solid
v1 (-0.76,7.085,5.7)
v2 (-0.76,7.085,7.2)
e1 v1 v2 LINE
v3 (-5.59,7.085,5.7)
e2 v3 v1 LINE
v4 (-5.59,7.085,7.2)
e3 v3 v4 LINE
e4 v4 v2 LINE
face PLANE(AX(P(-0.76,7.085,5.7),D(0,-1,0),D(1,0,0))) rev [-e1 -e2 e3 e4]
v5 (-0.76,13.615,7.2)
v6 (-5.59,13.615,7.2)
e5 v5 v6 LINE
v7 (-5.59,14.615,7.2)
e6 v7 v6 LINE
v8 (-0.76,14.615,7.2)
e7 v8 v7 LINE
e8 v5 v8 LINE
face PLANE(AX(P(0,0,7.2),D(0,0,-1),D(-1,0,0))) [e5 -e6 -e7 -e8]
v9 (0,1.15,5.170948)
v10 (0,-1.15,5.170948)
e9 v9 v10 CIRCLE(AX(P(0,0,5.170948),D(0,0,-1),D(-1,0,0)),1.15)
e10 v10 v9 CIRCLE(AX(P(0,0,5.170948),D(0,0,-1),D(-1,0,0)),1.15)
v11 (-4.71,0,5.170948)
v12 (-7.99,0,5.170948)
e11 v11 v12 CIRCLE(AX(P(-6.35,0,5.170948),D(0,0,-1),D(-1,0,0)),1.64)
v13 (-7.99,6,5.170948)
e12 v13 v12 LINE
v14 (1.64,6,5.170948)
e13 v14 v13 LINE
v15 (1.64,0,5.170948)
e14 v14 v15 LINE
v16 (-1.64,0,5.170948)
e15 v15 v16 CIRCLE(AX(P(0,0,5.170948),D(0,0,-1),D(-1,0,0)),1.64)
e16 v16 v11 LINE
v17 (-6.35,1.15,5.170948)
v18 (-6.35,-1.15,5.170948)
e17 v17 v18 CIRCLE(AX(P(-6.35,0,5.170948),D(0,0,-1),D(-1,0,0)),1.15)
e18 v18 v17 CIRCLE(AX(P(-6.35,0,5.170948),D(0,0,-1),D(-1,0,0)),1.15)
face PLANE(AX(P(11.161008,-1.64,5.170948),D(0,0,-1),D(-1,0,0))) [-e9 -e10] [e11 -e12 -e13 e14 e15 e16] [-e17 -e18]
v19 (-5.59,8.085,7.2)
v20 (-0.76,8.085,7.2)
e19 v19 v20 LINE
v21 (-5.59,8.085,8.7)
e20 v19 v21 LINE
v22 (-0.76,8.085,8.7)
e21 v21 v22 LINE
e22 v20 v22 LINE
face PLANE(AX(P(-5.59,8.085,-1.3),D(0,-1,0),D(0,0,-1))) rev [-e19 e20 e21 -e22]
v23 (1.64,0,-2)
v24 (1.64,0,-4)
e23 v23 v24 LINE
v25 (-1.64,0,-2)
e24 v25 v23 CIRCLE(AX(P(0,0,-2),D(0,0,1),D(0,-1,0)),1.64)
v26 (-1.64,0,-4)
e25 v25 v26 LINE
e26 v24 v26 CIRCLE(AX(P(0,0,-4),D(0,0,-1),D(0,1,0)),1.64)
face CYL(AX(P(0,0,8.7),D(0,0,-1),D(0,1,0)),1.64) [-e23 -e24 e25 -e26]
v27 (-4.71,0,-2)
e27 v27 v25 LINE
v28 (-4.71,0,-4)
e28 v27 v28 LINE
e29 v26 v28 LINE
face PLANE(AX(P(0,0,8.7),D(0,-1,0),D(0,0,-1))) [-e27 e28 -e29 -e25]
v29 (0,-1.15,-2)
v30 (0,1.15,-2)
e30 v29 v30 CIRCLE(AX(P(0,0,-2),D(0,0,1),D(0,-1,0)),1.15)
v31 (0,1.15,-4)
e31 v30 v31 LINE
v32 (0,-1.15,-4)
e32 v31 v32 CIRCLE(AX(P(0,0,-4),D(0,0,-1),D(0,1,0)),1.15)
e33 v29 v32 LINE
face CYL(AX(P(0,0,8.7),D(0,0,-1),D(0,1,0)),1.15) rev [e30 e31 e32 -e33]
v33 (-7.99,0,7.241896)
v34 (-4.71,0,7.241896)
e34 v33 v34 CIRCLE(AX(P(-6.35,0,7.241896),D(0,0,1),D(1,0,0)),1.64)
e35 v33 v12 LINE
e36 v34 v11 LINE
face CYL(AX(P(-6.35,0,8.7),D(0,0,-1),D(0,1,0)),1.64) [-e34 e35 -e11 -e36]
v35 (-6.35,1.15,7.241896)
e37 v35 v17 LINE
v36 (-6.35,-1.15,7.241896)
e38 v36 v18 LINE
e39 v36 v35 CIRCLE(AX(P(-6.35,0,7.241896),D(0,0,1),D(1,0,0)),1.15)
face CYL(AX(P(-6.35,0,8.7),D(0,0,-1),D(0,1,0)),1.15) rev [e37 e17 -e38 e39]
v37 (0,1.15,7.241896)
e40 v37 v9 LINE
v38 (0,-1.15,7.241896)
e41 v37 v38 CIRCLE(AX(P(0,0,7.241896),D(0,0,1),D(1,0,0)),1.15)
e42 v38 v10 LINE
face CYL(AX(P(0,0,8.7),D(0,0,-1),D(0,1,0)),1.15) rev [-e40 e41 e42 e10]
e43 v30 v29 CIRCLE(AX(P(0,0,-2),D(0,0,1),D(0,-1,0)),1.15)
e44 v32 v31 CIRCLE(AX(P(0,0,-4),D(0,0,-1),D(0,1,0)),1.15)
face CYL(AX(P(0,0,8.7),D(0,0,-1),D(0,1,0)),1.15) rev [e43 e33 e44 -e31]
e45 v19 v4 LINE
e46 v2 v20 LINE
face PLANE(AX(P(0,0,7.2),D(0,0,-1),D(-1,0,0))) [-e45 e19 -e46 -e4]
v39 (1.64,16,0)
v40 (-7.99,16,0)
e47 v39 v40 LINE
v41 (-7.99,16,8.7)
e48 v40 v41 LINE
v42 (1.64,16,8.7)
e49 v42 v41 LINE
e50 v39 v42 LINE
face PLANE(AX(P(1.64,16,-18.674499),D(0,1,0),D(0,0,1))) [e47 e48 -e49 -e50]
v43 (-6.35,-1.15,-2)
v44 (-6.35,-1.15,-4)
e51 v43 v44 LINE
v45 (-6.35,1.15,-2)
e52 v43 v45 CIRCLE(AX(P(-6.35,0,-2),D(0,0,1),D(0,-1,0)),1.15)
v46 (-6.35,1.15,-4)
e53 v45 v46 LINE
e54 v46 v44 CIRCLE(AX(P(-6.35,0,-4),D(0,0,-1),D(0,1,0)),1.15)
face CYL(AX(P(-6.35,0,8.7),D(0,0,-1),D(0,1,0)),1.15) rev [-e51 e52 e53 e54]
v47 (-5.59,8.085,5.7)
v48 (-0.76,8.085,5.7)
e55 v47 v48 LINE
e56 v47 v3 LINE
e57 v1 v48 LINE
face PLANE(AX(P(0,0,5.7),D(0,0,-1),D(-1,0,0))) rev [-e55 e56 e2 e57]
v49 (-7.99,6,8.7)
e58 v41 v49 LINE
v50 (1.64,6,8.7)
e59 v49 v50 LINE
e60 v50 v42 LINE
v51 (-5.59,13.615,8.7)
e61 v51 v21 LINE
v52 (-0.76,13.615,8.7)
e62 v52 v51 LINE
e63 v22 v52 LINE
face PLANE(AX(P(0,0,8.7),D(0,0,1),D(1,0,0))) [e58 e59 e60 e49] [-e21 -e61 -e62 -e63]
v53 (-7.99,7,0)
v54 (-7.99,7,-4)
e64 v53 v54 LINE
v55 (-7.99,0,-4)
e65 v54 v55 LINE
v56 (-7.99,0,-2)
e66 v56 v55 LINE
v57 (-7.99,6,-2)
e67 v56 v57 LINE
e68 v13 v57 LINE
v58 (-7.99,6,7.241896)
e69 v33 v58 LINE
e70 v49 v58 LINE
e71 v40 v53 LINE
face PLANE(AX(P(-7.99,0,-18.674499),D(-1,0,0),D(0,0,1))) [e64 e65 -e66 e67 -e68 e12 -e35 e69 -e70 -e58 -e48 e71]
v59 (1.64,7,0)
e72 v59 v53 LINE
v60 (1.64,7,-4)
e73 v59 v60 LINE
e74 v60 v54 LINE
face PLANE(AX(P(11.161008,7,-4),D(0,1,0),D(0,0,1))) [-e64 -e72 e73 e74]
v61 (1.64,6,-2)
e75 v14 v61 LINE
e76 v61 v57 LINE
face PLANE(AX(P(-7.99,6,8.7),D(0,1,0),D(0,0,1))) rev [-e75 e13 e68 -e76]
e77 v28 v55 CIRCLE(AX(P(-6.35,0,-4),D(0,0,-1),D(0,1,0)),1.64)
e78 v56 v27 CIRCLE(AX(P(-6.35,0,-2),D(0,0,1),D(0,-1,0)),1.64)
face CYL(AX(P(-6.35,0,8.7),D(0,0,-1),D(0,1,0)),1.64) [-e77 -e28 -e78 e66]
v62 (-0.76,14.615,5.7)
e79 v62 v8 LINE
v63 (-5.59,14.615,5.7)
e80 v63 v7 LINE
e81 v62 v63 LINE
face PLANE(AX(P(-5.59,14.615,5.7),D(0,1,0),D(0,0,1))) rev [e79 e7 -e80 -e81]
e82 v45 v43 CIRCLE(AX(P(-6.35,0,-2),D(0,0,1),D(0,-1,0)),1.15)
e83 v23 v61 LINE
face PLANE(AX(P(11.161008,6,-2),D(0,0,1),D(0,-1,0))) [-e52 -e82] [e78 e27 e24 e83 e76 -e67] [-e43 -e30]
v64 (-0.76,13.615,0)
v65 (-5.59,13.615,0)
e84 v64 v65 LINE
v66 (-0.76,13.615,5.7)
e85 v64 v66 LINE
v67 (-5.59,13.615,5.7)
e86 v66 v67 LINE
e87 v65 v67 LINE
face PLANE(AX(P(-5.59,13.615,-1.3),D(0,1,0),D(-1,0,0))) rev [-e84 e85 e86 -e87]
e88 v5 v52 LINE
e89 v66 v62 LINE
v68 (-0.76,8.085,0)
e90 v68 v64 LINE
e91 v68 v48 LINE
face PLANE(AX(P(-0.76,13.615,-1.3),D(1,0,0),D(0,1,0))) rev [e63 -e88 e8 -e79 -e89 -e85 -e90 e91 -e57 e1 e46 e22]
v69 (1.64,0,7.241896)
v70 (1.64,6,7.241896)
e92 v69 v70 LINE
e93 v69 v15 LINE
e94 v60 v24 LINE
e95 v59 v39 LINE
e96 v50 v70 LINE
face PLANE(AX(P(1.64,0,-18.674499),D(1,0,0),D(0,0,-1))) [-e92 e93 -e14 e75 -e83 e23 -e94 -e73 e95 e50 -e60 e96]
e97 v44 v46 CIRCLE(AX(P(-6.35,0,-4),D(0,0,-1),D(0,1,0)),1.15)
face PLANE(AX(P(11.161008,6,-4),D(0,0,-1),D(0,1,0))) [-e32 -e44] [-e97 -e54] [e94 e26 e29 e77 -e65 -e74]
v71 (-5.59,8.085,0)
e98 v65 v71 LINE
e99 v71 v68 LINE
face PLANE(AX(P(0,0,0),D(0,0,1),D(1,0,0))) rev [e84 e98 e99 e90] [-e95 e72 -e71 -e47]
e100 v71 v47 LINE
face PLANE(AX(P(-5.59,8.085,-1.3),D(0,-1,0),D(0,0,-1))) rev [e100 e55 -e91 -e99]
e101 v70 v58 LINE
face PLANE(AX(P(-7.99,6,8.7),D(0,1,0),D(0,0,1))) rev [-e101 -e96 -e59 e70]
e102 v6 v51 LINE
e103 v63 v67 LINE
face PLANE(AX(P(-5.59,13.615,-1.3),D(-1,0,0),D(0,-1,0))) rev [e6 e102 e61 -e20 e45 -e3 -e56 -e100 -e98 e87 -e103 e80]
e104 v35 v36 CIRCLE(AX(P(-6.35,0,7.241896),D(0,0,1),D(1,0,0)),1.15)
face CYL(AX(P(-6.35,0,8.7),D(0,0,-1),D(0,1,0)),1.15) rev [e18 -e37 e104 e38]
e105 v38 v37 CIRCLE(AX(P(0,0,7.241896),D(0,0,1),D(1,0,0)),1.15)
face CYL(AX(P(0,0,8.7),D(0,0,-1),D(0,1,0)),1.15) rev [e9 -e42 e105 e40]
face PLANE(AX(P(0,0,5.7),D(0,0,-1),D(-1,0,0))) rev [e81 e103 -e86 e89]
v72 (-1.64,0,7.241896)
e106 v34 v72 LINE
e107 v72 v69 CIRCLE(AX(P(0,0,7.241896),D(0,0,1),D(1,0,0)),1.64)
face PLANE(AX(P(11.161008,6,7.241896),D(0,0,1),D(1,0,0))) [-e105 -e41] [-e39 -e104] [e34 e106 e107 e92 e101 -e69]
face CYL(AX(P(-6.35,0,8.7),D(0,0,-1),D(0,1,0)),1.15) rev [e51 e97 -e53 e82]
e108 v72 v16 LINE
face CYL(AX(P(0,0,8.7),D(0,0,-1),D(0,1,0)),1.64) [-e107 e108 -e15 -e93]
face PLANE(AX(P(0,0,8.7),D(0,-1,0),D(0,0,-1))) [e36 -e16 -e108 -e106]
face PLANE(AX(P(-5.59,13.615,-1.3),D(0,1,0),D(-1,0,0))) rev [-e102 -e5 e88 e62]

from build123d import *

# Parameters (mm, degrees)
SKETCH_1_R          = 1.64
SKETCH_1_R_2        = 1.15
EXTRUDE_1_DEPTH     = 3.1
EXTRUDE_1_2_DEPTH   = 3.1
EXTRUDE_START       = -3.1
EXTRUDE_2_DEPTH     = 3.1
SKETCH_4_W          = 9.63
SKETCH_4_H          = 10
EXTRUDE_3_DEPTH     = 5.6
SKETCH_5_W          = 4.83
SKETCH_5_H          = 5.53
CUT_EXTRUDE_1_DEPTH = 10
SKETCH_6_W          = 4.83
SKETCH_6_H          = 7.53
CUT_EXTRUDE_2_DEPTH = 1.5
SKETCH_7_W          = 2.070948157
SKETCH_7_H          = 7.64
EXTRUDE_4_DEPTH     = 9.63
SKETCH_10_R         = 1.15
CUT_EXTRUDE_3_DEPTH = 22.934678024
SKETCH_11_W         = 3.1
SKETCH_11_H         = 7.64
CUT_EXTRUDE_4_DEPTH = 21.601623722
CUT_EXTRUDE_5_DEPTH = 22.934678024


with BuildPart() as part:
    # 草图1 → 凸台-拉伸1 (new body)
    with BuildSketch(Plane.XY):
        with Locations(Location((0, 0, 0), (0, 0, 180))):
            Circle(SKETCH_1_R)
        with Locations(Location((0, 0, 0), (0, 0, 180))):
            Circle(SKETCH_1_R_2, mode=Mode.SUBTRACT)
    extrude(amount=EXTRUDE_1_DEPTH)



with BuildPart() as body_2:
    # 草图1 → Extrude 1 2 (new body)
    with BuildSketch(Plane.XY):
        with Locations(Location((-6.35, 0, 0), (0, 0, 180))):
            Circle(SKETCH_1_R)
        with Locations(Location((-6.35, 0, 0), (0, 0, 180))):
            Circle(SKETCH_1_R_2, mode=Mode.SUBTRACT)
    extrude(amount=EXTRUDE_1_2_DEPTH)


with BuildPart() as part_1:
    add(part.part)

    add(body_2.part)  # 凸台-拉伸2 merges body 2
    # 草图2 → 凸台-拉伸2 (add)
    with BuildSketch(Plane.XY.offset(3.1).offset(EXTRUDE_START)):
        with BuildLine():
            Line((-7.99, 0), (-7.99, 16))
            Line((-7.99, 16), (1.64, 16))
            Line((1.64, 16), (1.64, 0))
            ThreePointArc((1.64, 0), (0, 1.64), (-1.64, 0))
            Line((-1.64, 0), (-4.71, 0))
            ThreePointArc((-4.71, 0), (-6.35, 1.64), (-7.99, 0))
        make_face()
    extrude(amount=EXTRUDE_2_DEPTH)

    # 草图4 → 凸台-拉伸3 (add)
    with BuildSketch(Plane.XY.offset(3.1)):
        with Locations((-3.175, 11)):
            Rectangle(SKETCH_4_W, SKETCH_4_H)
    extrude(amount=EXTRUDE_3_DEPTH)

    # 草图5 → 切除-拉伸1 (cut)
    with BuildSketch(Plane.XY.offset(8.7)):
        with Locations((-3.175, 10.85)):
            Rectangle(SKETCH_5_W, SKETCH_5_H)
    extrude(amount=-CUT_EXTRUDE_1_DEPTH, mode=Mode.SUBTRACT)

    # 草图6 → 切除-拉伸2 (cut)
    with BuildSketch(Plane.XY.offset(7.2)):
        with Locations((-3.175, 10.85)):
            Rectangle(SKETCH_6_W, SKETCH_6_H)
    extrude(amount=-CUT_EXTRUDE_2_DEPTH, mode=Mode.SUBTRACT)

    # 草图7 → 凸台-拉伸4 (add)
    with BuildSketch(Plane.ZY.offset(7.99)):
        with Locations((6.206422236, 2.18)):
            Rectangle(SKETCH_7_W, SKETCH_7_H)
        Polygon((0, 6), (-2, 6), (-2, -1.64), (-4, -1.64), (-4, 6), (-4, 7), (0, 7), align=None)
    extrude(amount=-EXTRUDE_4_DEPTH)

    # 草图10 → 切除-拉伸3 (cut, through all)
    with BuildSketch(Plane(origin=(0, 0, -4), x_dir=(-1, 0, 0), z_dir=(0, 0, -1))):
        Circle(SKETCH_10_R)
        with Locations((6.35, 0)):
            Circle(SKETCH_10_R)
    extrude(amount=-CUT_EXTRUDE_3_DEPTH, mode=Mode.SUBTRACT)

    # 草图11 → 切除-拉伸4 (cut, through all)
    with BuildSketch(Plane(origin=(1.64, 0, 0), x_dir=(0, 0, -1), z_dir=(1, 0, 0))):
        with Locations((-1.55, 2.18)):
            Rectangle(SKETCH_11_W, SKETCH_11_H)
    extrude(amount=-CUT_EXTRUDE_4_DEPTH, mode=Mode.SUBTRACT)

    # 草图12 → 切除-拉伸5 (cut, through all)
    with BuildSketch(Plane(origin=(0, 0, -4), x_dir=(-1, 0, 0), z_dir=(0, 0, -1))):
        with BuildLine():
            Line((4.71, 0), (1.64, 0))
            ThreePointArc((1.64, 0), (1.159655121, -1.159655121), (0, -1.64))
            Line((0, -1.64), (6.35, -1.64))
            ThreePointArc((6.35, -1.64), (5.190344879, -1.159655121), (4.71, 0))
        make_face()
        with BuildLine():
            Line((-1.64, -1.64), (0, -1.64))
            ThreePointArc((0, -1.64), (-1.159655121, -1.159655121), (-1.64, 0))
            Line((-1.64, 0), (-1.64, -1.64))
        make_face()
        with BuildLine():
            ThreePointArc((7.99, 0), (7.509655121, -1.159655121), (6.35, -1.64))
            Line((6.35, -1.64), (7.99, -1.64))
            Line((7.99, -1.64), (7.99, 0))
        make_face()
    extrude(amount=-CUT_EXTRUDE_5_DEPTH, mode=Mode.SUBTRACT)


solid = part_1.part
